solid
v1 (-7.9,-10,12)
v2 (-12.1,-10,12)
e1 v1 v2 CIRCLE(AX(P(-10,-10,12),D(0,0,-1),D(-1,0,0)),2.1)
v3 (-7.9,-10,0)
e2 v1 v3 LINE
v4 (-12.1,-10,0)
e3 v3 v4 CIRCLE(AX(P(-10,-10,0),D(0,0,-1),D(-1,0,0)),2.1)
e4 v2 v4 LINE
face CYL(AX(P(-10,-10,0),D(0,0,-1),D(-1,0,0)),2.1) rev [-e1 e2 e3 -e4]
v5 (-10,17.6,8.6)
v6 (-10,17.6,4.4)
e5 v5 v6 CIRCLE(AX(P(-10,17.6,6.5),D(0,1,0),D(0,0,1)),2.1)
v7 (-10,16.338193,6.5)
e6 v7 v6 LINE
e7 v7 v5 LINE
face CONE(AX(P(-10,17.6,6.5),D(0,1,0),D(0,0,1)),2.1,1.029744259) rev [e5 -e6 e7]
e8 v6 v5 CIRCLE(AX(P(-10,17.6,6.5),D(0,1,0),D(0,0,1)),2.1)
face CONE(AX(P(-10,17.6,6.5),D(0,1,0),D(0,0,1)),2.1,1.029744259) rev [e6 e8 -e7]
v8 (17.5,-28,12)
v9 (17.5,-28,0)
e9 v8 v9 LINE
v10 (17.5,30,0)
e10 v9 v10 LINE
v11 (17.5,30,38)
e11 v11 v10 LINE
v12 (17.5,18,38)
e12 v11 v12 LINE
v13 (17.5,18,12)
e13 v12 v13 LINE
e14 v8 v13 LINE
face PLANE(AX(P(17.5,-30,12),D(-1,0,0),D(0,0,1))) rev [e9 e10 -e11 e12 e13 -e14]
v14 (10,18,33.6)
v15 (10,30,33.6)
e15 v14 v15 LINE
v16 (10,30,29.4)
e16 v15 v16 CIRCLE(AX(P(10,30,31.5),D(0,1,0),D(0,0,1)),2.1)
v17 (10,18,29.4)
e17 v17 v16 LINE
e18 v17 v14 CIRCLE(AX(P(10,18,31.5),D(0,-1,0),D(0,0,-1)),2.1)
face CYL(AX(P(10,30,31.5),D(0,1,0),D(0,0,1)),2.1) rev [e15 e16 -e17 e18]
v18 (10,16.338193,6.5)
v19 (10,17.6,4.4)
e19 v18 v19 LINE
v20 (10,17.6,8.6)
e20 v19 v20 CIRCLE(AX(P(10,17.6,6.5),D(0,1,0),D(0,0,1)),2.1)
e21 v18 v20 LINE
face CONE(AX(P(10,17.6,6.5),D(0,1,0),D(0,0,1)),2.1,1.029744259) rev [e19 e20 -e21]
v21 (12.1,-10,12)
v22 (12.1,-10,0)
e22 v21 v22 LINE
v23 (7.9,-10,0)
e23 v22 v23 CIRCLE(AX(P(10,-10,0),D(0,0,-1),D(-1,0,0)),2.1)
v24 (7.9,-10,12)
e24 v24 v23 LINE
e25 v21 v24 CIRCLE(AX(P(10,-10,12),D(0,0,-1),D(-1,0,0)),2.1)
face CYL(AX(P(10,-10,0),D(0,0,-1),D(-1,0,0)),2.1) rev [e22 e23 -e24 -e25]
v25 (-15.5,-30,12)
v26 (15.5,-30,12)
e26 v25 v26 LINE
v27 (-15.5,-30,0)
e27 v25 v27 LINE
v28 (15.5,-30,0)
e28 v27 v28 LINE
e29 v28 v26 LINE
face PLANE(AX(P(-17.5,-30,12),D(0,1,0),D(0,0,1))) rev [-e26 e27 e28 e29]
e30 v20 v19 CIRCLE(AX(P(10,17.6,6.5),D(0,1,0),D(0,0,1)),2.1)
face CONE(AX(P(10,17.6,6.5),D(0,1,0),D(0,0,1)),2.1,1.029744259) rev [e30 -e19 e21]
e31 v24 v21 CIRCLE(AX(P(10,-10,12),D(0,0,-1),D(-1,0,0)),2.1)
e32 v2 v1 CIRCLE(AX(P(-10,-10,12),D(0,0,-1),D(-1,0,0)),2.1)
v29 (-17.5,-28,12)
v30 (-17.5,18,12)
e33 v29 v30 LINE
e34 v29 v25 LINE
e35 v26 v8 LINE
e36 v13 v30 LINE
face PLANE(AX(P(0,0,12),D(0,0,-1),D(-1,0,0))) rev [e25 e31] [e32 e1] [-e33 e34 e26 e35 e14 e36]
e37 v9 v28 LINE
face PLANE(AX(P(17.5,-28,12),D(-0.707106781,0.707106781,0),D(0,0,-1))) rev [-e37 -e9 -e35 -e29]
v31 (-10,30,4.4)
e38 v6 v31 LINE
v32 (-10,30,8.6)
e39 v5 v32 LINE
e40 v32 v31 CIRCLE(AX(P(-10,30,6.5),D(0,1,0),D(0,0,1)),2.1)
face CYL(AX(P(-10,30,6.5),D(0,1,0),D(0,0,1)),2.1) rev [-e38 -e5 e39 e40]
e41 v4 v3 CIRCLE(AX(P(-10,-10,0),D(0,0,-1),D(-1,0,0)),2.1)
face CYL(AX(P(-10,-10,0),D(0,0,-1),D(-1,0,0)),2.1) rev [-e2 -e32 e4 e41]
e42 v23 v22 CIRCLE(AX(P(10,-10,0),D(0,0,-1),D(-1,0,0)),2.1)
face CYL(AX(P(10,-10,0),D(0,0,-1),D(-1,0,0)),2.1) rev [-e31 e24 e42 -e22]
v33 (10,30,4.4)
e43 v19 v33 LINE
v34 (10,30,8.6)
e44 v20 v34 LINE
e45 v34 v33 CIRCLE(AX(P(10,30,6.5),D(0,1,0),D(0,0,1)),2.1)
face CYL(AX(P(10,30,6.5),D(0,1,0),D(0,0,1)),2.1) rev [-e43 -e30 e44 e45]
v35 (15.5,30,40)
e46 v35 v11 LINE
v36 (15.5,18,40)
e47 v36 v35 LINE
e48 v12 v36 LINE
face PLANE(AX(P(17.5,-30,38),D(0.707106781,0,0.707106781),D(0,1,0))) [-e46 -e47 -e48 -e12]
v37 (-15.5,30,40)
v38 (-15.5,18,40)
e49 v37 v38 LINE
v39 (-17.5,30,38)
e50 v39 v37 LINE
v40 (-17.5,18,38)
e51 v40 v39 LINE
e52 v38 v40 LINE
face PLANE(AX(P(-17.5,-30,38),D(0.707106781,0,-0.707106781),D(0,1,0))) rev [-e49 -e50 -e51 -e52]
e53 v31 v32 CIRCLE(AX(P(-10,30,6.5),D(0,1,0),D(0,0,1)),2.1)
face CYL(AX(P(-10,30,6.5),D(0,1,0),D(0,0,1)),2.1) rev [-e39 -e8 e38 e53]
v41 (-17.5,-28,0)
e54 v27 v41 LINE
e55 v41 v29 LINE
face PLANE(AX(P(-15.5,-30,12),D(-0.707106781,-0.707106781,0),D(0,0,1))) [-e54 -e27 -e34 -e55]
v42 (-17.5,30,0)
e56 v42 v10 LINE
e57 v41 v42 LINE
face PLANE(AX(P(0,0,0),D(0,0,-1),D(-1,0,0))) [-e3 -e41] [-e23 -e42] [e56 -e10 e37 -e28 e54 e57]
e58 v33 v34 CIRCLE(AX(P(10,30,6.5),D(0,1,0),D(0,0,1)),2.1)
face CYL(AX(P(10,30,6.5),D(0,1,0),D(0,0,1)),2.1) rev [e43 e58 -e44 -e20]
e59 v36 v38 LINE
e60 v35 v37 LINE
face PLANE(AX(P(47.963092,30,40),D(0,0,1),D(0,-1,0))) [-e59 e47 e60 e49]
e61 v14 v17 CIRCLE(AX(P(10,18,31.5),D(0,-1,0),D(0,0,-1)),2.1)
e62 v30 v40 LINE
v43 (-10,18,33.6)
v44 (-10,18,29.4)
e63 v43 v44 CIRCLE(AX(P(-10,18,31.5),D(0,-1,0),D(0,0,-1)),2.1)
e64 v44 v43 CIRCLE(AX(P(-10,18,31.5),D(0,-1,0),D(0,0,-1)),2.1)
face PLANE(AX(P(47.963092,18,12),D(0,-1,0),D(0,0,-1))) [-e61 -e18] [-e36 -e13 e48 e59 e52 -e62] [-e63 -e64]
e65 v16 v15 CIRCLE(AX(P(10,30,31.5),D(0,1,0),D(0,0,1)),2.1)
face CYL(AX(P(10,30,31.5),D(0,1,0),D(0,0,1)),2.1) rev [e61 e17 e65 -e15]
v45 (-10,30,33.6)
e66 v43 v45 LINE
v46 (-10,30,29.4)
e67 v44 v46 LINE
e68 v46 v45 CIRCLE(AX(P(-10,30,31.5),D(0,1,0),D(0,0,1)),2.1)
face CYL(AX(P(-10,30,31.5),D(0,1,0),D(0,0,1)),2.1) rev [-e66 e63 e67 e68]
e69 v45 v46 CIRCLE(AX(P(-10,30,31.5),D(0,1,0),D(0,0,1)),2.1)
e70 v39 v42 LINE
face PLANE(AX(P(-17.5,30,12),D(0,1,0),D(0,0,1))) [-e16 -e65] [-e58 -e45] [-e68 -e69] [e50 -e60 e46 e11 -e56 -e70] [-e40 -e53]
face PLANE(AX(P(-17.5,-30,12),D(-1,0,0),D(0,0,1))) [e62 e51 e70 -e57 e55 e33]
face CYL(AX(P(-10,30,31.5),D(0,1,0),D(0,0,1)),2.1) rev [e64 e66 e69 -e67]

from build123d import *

# Parameters (mm, degrees)
SKETCH_1_W             = 35
SKETCH_1_H             = 60
EXTRUDE_1_DEPTH        = 12
CHAMFER_1_SIZE         = 2
SKETCH_4_W             = 28
SKETCH_4_H             = 12
EXTRUDE_2_DEPTH        = 35
HOLE_WIZARD_M5_1_D     = 4.2
CHAMFER_2_SIZE         = 2
HOLE_WIZARD_M5_2_D     = 4.2
HOLE_WIZARD_M5_2_DEPTH = 12.4
HOLE_WIZARD_M5_2_TIP   = 1.2618073


with BuildPart() as part:
    # 草图1 → 凸台-拉伸1 (new body)
    with BuildSketch(Plane.XY):
        Rectangle(SKETCH_1_W, SKETCH_1_H)
    extrude(amount=EXTRUDE_1_DEPTH)

    # 倒角1
    chamfer_1_edges = [part.edges().sort_by_distance(p)[0] for p in [
        (-17.5, -30, 6),
        (17.5, -30, 6),
    ]]
    chamfer(chamfer_1_edges, length=CHAMFER_1_SIZE)

    # 草图4 → 凸台-拉伸2 (add)
    with BuildSketch(Plane.ZY.offset(17.5)):
        with Locations((26, 24)):
            Rectangle(SKETCH_4_W, SKETCH_4_H)
    extrude(amount=-EXTRUDE_2_DEPTH)

    # M5 螺纹孔1 (through all)
    with Locations(Plane(origin=(0, 0, 0), x_dir=(-1, 0, 0), z_dir=(0, 0, -1))):
        with Locations((-10, -10), (10, -10)):
            Hole(HOLE_WIZARD_M5_1_D / 2)

    # 倒角2
    chamfer_2_edges = [part.edges().sort_by_distance(p)[0] for p in [
        (-17.5, 24, 40),
        (17.5, 24, 40),
    ]]
    chamfer(chamfer_2_edges, length=CHAMFER_2_SIZE)

    # M5 螺纹孔2
    with Locations(Plane(origin=(0, 30, 0), x_dir=(1, 0, 0), z_dir=(0, 1, 0))):
        with Locations((-10, -6.5), (10, -6.5), (-10, -31.5), (10, -31.5)):
            Hole(HOLE_WIZARD_M5_2_D / 2, depth=HOLE_WIZARD_M5_2_DEPTH)
            with Locations((0, 0, -(HOLE_WIZARD_M5_2_DEPTH + HOLE_WIZARD_M5_2_TIP / 2))):  # 118° drill point
                Cone(0, HOLE_WIZARD_M5_2_D / 2, HOLE_WIZARD_M5_2_TIP, mode=Mode.SUBTRACT)


solid = part.part
